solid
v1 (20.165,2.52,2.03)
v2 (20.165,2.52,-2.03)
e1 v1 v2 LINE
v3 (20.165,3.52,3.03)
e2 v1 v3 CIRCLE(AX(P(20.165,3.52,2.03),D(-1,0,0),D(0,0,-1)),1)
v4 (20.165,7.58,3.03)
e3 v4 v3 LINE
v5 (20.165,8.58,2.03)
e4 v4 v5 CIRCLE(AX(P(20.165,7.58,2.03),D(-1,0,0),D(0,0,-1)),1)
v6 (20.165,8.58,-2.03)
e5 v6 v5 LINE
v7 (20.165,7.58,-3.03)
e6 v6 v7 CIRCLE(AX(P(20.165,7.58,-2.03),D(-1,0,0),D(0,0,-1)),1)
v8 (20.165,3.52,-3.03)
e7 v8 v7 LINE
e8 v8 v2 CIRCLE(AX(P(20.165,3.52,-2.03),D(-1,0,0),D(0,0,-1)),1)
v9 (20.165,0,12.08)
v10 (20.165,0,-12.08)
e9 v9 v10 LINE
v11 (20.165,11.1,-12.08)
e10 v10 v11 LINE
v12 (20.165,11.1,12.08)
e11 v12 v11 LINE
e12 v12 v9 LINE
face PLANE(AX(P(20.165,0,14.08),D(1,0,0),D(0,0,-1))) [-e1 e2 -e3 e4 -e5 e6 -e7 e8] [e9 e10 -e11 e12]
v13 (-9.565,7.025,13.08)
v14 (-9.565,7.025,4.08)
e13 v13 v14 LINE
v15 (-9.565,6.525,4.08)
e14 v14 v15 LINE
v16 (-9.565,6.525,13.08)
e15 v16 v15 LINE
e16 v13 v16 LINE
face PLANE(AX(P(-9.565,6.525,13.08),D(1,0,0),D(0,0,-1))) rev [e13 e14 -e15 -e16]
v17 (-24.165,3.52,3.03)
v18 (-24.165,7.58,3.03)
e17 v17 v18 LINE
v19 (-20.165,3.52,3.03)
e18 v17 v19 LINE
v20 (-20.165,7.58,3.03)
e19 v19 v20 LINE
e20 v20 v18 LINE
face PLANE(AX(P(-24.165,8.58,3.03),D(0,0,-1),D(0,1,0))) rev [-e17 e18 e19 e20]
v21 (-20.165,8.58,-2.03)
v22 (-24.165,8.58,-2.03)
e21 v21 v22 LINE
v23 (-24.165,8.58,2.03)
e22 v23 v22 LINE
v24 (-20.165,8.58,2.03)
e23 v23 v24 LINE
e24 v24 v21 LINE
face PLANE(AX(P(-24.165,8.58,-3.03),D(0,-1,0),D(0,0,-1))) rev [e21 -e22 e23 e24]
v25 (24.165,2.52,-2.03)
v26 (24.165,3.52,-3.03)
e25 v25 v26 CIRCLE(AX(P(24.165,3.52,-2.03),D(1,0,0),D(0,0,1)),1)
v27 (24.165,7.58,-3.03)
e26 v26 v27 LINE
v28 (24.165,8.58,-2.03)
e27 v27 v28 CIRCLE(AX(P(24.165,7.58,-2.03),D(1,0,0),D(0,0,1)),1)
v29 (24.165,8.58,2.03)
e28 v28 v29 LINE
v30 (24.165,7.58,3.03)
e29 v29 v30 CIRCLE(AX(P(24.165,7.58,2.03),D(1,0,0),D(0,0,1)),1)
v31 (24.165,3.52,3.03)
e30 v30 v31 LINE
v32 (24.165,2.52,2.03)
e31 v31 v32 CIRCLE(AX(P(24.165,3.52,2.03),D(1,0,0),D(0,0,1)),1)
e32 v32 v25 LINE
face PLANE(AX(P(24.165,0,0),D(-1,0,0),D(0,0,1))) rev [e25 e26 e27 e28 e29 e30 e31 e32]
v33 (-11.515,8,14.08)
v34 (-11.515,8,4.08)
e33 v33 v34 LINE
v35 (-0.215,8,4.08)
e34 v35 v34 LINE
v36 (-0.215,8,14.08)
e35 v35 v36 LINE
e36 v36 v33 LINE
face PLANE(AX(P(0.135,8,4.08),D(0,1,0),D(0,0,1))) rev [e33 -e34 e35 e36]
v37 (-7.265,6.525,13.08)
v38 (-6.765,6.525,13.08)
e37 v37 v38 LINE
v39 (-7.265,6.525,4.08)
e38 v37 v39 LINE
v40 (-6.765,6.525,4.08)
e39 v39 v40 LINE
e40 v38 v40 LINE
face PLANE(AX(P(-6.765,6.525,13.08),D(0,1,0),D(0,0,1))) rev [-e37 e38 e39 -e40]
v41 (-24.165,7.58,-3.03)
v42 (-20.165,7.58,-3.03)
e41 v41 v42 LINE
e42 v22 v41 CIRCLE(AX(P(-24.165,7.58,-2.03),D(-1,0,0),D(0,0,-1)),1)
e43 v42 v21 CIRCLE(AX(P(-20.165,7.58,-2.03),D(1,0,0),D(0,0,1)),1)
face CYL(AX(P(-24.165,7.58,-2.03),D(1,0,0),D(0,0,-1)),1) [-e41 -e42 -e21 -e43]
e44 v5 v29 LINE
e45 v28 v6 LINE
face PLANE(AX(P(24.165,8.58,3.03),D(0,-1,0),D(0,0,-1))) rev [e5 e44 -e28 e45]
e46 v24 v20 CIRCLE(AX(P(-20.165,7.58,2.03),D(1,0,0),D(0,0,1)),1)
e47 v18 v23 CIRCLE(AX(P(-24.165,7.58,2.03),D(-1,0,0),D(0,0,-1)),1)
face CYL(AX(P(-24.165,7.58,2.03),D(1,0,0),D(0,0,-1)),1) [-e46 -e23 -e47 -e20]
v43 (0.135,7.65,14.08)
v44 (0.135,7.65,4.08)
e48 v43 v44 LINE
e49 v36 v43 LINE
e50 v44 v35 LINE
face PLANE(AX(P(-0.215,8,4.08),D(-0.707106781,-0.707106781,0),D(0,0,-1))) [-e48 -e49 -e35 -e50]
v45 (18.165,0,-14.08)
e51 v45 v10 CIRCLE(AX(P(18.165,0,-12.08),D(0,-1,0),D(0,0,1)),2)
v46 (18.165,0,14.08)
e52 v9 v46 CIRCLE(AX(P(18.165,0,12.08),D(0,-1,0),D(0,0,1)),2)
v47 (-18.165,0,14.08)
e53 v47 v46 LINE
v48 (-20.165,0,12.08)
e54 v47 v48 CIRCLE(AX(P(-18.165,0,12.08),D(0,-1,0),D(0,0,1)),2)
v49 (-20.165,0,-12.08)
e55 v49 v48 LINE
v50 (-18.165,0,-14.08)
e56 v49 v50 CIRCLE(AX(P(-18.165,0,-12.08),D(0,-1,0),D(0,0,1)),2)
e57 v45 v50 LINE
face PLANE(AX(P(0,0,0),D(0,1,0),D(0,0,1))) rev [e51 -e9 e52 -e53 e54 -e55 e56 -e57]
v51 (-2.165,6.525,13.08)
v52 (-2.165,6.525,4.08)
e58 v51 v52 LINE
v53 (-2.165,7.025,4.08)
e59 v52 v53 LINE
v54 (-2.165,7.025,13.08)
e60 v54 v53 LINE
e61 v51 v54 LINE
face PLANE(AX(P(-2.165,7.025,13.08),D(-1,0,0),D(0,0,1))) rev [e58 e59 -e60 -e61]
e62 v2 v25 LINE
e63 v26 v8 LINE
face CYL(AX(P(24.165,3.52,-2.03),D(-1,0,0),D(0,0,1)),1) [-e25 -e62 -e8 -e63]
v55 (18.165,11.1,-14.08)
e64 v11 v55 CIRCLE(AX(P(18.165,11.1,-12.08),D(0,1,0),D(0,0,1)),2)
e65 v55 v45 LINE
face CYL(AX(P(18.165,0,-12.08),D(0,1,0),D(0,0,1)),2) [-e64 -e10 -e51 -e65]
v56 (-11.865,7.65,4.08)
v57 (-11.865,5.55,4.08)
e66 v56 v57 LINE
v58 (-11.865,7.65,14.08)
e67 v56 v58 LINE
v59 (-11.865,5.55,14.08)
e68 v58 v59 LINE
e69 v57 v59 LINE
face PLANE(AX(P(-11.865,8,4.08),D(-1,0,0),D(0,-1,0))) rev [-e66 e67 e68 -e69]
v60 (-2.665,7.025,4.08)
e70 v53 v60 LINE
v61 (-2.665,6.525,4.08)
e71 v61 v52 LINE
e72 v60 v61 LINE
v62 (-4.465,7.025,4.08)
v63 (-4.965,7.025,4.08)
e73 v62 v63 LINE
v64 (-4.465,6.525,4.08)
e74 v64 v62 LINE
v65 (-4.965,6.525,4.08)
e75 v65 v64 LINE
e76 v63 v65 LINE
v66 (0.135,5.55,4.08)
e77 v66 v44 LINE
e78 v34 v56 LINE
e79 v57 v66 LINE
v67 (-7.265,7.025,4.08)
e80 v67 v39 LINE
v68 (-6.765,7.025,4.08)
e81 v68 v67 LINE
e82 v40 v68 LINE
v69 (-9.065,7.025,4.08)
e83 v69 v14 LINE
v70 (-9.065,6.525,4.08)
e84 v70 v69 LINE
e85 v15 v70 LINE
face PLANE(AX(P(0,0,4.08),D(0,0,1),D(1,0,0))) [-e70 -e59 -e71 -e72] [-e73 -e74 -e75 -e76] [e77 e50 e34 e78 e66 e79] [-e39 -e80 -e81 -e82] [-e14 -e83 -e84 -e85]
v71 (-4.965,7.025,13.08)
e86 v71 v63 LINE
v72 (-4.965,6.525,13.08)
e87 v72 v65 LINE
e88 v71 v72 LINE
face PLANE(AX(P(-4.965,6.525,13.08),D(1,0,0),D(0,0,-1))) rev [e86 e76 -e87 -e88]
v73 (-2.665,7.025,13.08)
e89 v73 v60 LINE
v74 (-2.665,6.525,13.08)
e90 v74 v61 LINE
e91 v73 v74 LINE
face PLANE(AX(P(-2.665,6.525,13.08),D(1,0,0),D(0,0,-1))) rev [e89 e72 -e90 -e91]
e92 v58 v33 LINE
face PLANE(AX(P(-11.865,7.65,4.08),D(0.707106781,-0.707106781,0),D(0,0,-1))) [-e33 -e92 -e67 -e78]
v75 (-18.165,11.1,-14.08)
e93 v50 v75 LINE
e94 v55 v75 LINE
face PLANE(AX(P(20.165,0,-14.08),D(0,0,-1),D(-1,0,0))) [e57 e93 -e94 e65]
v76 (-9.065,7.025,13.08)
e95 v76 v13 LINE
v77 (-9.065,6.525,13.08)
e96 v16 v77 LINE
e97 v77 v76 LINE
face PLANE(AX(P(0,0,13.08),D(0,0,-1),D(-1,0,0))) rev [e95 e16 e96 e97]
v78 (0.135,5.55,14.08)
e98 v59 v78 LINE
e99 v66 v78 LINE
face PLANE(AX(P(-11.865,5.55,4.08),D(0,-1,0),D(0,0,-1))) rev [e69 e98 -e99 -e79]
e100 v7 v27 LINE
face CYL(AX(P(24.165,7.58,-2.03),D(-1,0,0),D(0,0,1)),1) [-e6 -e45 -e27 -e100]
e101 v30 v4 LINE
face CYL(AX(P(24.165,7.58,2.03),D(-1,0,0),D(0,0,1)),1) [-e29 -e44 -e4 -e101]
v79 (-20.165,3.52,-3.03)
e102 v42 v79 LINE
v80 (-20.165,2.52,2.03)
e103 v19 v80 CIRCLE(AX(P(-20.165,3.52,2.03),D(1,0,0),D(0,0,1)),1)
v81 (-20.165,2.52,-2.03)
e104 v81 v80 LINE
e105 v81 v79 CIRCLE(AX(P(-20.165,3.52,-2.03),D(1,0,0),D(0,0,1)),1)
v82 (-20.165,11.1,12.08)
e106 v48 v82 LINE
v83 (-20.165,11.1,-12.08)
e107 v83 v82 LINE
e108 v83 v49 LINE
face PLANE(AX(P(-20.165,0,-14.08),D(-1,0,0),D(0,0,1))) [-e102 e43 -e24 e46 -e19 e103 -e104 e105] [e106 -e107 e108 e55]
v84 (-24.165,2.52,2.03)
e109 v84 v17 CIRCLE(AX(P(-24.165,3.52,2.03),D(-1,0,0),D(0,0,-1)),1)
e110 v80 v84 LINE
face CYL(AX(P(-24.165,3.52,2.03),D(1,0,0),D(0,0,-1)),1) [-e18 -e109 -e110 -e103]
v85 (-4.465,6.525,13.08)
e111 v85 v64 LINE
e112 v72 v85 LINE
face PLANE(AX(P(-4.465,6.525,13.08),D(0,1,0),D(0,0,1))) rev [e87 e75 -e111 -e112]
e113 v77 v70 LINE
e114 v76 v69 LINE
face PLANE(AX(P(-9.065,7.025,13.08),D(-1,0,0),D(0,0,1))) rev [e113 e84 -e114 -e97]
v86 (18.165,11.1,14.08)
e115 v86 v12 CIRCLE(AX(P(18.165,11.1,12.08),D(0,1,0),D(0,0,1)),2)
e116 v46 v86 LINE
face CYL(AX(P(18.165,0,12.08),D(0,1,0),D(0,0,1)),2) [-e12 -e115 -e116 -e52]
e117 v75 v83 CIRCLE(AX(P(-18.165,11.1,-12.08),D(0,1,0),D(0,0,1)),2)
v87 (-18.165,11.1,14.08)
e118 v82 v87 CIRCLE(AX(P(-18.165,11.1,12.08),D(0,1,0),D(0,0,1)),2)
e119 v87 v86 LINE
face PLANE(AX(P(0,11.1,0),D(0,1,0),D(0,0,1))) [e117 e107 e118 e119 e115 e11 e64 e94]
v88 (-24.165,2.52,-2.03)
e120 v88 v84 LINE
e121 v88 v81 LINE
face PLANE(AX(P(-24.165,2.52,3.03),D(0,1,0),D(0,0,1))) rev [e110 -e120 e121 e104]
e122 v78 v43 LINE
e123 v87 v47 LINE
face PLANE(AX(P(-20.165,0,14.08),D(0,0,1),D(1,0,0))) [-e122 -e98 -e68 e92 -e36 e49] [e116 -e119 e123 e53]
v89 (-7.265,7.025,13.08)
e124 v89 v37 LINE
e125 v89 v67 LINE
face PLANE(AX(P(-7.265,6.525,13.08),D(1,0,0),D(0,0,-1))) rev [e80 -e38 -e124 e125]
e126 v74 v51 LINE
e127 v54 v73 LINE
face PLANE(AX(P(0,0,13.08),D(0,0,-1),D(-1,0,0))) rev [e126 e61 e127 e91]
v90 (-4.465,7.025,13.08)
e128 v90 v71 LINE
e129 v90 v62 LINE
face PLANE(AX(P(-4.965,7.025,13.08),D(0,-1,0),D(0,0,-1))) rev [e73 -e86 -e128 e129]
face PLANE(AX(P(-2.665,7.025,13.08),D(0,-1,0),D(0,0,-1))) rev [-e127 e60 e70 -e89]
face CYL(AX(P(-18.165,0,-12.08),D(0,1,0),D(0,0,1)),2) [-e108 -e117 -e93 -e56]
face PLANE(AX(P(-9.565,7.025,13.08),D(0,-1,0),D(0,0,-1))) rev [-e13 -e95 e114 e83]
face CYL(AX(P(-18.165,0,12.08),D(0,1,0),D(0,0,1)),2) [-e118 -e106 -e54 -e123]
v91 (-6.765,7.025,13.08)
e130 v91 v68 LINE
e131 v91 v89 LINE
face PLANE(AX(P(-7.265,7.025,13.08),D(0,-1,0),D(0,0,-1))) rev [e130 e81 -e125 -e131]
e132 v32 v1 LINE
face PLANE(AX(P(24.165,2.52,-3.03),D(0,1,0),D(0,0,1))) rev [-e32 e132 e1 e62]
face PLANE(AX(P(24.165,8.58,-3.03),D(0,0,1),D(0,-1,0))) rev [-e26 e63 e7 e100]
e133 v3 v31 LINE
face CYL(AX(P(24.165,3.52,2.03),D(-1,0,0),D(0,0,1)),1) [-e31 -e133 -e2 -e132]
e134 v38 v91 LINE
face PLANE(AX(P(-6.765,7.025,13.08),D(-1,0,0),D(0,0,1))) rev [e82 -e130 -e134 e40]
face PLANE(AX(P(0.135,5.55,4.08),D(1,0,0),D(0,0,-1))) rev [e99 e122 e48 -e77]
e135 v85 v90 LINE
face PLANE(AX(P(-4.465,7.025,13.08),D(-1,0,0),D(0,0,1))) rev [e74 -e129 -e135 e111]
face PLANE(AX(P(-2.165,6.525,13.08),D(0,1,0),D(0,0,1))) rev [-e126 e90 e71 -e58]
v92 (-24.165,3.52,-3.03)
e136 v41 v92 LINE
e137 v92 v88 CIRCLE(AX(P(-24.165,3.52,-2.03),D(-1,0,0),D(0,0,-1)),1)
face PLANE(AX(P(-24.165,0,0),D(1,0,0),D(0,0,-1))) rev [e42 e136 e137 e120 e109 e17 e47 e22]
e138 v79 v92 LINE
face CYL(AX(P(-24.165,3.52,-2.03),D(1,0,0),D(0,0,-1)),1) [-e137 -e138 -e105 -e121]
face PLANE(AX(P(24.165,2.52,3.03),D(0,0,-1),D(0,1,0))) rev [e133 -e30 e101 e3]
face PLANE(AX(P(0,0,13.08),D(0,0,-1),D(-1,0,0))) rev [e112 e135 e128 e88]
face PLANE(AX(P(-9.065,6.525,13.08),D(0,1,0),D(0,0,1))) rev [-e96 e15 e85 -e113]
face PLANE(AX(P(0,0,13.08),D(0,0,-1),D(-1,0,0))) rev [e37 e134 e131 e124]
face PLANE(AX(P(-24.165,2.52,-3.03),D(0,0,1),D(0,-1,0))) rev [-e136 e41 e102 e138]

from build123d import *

# Parameters (mm, degrees)
SKETCH_1_W          = 40.33
SKETCH_1_H          = 28.16
EXTRUDE_1_DEPTH     = 11.1
SKETCH_2_W          = 12
SKETCH_2_H          = 2.45
CUT_EXTRUDE_1_DEPTH = 10
SKETCH_3_W          = 0.5
SKETCH_3_H          = 0.5
EXTRUDE_2_DEPTH     = 9
SKETCH_4_W          = 0.5
SKETCH_4_H          = 0.5
EXTRUDE_3_DEPTH     = 9
SKETCH_5_W          = 0.5
SKETCH_5_H          = 0.5
EXTRUDE_4_DEPTH     = 9
SKETCH_6_W          = 0.5
SKETCH_6_H          = 0.5
EXTRUDE_5_DEPTH     = 9
SKETCH_7_W          = 6.06
SKETCH_7_H          = 6.06
EXTRUDE_6_DEPTH     = 4
SKETCH_8_W          = 6.06
SKETCH_8_H          = 6.06
EXTRUDE_7_DEPTH     = 4
CHAMFER_1_SIZE      = 0.35
FILLET_1_R          = 1
FILLET_2_R          = 2


with BuildPart() as part:
    # 草图1 → 凸台-拉伸1 (new body)
    with BuildSketch(Plane(origin=(0, 11.1, 0), x_dir=(1, 0, 0), z_dir=(0, 1, 0))):
        Rectangle(SKETCH_1_W, SKETCH_1_H)
    extrude(amount=-EXTRUDE_1_DEPTH)

    # 草图2 → 切除-拉伸1 (cut)
    with BuildSketch(Plane.XY.offset(14.08)):
        with Locations((-5.865, 6.775)):
            Rectangle(SKETCH_2_W, SKETCH_2_H)
    extrude(amount=-CUT_EXTRUDE_1_DEPTH, mode=Mode.SUBTRACT)

    # 草图3 → 凸台-拉伸2 (add)
    with BuildSketch(Plane.XY.offset(4.08)):
        with Locations((-4.715, 6.775)):
            Rectangle(SKETCH_3_W, SKETCH_3_H)
    extrude(amount=EXTRUDE_2_DEPTH)

    # 草图4 → 凸台-拉伸3 (add)
    with BuildSketch(Plane.XY.offset(4.08)):
        with Locations((-9.315, 6.775)):
            Rectangle(SKETCH_4_W, SKETCH_4_H)
    extrude(amount=EXTRUDE_3_DEPTH)

    # 草图5 → 凸台-拉伸4 (add)
    with BuildSketch(Plane.XY.offset(4.08)):
        with Locations((-7.015, 6.775)):
            Rectangle(SKETCH_5_W, SKETCH_5_H)
    extrude(amount=EXTRUDE_4_DEPTH)

    # 草图6 → 凸台-拉伸5 (add)
    with BuildSketch(Plane.XY.offset(4.08)):
        with Locations((-2.415, 6.775)):
            Rectangle(SKETCH_6_W, SKETCH_6_H)
    extrude(amount=EXTRUDE_5_DEPTH)

    # 草图7 → 凸台-拉伸6 (add)
    with BuildSketch(Plane.ZY.offset(20.165)):
        with Locations((0, 5.55)):
            Rectangle(SKETCH_7_W, SKETCH_7_H)
    extrude(amount=EXTRUDE_6_DEPTH)

    # 草图8 → 凸台-拉伸7 (add)
    with BuildSketch(Plane(origin=(20.165, 0, 0), x_dir=(0, 0, -1), z_dir=(1, 0, 0))):
        with Locations((0, 5.55)):
            Rectangle(SKETCH_8_W, SKETCH_8_H)
    extrude(amount=EXTRUDE_7_DEPTH)

    # 倒角1
    chamfer_1_edges = [part.edges().sort_by_distance(p)[0] for p in [
        (-11.865, 8, 9.08),
        (0.135, 8, 9.08),
    ]]
    chamfer(chamfer_1_edges, length=CHAMFER_1_SIZE)

    # 圆角1
    fillet_1_edges = [part.edges().sort_by_distance(p)[0] for p in [
        (-22.165, 2.52, -3.03),
        (-22.165, 2.52, 3.03),
        (-22.165, 8.58, 3.03),
        (-22.165, 8.58, -3.03),
        (22.165, 2.52, 3.03),
        (22.165, 2.52, -3.03),
        (22.165, 8.58, -3.03),
        (22.165, 8.58, 3.03),
    ]]
    fillet(fillet_1_edges, radius=FILLET_1_R)

    # 圆角2
    fillet_2_edges = [part.edges().sort_by_distance(p)[0] for p in [
        (20.165, 5.55, -14.08),
        (20.165, 5.55, 14.08),
        (-20.165, 5.55, 14.08),
        (-20.165, 5.55, -14.08),
    ]]
    fillet(fillet_2_edges, radius=FILLET_2_R)


solid = part.part
